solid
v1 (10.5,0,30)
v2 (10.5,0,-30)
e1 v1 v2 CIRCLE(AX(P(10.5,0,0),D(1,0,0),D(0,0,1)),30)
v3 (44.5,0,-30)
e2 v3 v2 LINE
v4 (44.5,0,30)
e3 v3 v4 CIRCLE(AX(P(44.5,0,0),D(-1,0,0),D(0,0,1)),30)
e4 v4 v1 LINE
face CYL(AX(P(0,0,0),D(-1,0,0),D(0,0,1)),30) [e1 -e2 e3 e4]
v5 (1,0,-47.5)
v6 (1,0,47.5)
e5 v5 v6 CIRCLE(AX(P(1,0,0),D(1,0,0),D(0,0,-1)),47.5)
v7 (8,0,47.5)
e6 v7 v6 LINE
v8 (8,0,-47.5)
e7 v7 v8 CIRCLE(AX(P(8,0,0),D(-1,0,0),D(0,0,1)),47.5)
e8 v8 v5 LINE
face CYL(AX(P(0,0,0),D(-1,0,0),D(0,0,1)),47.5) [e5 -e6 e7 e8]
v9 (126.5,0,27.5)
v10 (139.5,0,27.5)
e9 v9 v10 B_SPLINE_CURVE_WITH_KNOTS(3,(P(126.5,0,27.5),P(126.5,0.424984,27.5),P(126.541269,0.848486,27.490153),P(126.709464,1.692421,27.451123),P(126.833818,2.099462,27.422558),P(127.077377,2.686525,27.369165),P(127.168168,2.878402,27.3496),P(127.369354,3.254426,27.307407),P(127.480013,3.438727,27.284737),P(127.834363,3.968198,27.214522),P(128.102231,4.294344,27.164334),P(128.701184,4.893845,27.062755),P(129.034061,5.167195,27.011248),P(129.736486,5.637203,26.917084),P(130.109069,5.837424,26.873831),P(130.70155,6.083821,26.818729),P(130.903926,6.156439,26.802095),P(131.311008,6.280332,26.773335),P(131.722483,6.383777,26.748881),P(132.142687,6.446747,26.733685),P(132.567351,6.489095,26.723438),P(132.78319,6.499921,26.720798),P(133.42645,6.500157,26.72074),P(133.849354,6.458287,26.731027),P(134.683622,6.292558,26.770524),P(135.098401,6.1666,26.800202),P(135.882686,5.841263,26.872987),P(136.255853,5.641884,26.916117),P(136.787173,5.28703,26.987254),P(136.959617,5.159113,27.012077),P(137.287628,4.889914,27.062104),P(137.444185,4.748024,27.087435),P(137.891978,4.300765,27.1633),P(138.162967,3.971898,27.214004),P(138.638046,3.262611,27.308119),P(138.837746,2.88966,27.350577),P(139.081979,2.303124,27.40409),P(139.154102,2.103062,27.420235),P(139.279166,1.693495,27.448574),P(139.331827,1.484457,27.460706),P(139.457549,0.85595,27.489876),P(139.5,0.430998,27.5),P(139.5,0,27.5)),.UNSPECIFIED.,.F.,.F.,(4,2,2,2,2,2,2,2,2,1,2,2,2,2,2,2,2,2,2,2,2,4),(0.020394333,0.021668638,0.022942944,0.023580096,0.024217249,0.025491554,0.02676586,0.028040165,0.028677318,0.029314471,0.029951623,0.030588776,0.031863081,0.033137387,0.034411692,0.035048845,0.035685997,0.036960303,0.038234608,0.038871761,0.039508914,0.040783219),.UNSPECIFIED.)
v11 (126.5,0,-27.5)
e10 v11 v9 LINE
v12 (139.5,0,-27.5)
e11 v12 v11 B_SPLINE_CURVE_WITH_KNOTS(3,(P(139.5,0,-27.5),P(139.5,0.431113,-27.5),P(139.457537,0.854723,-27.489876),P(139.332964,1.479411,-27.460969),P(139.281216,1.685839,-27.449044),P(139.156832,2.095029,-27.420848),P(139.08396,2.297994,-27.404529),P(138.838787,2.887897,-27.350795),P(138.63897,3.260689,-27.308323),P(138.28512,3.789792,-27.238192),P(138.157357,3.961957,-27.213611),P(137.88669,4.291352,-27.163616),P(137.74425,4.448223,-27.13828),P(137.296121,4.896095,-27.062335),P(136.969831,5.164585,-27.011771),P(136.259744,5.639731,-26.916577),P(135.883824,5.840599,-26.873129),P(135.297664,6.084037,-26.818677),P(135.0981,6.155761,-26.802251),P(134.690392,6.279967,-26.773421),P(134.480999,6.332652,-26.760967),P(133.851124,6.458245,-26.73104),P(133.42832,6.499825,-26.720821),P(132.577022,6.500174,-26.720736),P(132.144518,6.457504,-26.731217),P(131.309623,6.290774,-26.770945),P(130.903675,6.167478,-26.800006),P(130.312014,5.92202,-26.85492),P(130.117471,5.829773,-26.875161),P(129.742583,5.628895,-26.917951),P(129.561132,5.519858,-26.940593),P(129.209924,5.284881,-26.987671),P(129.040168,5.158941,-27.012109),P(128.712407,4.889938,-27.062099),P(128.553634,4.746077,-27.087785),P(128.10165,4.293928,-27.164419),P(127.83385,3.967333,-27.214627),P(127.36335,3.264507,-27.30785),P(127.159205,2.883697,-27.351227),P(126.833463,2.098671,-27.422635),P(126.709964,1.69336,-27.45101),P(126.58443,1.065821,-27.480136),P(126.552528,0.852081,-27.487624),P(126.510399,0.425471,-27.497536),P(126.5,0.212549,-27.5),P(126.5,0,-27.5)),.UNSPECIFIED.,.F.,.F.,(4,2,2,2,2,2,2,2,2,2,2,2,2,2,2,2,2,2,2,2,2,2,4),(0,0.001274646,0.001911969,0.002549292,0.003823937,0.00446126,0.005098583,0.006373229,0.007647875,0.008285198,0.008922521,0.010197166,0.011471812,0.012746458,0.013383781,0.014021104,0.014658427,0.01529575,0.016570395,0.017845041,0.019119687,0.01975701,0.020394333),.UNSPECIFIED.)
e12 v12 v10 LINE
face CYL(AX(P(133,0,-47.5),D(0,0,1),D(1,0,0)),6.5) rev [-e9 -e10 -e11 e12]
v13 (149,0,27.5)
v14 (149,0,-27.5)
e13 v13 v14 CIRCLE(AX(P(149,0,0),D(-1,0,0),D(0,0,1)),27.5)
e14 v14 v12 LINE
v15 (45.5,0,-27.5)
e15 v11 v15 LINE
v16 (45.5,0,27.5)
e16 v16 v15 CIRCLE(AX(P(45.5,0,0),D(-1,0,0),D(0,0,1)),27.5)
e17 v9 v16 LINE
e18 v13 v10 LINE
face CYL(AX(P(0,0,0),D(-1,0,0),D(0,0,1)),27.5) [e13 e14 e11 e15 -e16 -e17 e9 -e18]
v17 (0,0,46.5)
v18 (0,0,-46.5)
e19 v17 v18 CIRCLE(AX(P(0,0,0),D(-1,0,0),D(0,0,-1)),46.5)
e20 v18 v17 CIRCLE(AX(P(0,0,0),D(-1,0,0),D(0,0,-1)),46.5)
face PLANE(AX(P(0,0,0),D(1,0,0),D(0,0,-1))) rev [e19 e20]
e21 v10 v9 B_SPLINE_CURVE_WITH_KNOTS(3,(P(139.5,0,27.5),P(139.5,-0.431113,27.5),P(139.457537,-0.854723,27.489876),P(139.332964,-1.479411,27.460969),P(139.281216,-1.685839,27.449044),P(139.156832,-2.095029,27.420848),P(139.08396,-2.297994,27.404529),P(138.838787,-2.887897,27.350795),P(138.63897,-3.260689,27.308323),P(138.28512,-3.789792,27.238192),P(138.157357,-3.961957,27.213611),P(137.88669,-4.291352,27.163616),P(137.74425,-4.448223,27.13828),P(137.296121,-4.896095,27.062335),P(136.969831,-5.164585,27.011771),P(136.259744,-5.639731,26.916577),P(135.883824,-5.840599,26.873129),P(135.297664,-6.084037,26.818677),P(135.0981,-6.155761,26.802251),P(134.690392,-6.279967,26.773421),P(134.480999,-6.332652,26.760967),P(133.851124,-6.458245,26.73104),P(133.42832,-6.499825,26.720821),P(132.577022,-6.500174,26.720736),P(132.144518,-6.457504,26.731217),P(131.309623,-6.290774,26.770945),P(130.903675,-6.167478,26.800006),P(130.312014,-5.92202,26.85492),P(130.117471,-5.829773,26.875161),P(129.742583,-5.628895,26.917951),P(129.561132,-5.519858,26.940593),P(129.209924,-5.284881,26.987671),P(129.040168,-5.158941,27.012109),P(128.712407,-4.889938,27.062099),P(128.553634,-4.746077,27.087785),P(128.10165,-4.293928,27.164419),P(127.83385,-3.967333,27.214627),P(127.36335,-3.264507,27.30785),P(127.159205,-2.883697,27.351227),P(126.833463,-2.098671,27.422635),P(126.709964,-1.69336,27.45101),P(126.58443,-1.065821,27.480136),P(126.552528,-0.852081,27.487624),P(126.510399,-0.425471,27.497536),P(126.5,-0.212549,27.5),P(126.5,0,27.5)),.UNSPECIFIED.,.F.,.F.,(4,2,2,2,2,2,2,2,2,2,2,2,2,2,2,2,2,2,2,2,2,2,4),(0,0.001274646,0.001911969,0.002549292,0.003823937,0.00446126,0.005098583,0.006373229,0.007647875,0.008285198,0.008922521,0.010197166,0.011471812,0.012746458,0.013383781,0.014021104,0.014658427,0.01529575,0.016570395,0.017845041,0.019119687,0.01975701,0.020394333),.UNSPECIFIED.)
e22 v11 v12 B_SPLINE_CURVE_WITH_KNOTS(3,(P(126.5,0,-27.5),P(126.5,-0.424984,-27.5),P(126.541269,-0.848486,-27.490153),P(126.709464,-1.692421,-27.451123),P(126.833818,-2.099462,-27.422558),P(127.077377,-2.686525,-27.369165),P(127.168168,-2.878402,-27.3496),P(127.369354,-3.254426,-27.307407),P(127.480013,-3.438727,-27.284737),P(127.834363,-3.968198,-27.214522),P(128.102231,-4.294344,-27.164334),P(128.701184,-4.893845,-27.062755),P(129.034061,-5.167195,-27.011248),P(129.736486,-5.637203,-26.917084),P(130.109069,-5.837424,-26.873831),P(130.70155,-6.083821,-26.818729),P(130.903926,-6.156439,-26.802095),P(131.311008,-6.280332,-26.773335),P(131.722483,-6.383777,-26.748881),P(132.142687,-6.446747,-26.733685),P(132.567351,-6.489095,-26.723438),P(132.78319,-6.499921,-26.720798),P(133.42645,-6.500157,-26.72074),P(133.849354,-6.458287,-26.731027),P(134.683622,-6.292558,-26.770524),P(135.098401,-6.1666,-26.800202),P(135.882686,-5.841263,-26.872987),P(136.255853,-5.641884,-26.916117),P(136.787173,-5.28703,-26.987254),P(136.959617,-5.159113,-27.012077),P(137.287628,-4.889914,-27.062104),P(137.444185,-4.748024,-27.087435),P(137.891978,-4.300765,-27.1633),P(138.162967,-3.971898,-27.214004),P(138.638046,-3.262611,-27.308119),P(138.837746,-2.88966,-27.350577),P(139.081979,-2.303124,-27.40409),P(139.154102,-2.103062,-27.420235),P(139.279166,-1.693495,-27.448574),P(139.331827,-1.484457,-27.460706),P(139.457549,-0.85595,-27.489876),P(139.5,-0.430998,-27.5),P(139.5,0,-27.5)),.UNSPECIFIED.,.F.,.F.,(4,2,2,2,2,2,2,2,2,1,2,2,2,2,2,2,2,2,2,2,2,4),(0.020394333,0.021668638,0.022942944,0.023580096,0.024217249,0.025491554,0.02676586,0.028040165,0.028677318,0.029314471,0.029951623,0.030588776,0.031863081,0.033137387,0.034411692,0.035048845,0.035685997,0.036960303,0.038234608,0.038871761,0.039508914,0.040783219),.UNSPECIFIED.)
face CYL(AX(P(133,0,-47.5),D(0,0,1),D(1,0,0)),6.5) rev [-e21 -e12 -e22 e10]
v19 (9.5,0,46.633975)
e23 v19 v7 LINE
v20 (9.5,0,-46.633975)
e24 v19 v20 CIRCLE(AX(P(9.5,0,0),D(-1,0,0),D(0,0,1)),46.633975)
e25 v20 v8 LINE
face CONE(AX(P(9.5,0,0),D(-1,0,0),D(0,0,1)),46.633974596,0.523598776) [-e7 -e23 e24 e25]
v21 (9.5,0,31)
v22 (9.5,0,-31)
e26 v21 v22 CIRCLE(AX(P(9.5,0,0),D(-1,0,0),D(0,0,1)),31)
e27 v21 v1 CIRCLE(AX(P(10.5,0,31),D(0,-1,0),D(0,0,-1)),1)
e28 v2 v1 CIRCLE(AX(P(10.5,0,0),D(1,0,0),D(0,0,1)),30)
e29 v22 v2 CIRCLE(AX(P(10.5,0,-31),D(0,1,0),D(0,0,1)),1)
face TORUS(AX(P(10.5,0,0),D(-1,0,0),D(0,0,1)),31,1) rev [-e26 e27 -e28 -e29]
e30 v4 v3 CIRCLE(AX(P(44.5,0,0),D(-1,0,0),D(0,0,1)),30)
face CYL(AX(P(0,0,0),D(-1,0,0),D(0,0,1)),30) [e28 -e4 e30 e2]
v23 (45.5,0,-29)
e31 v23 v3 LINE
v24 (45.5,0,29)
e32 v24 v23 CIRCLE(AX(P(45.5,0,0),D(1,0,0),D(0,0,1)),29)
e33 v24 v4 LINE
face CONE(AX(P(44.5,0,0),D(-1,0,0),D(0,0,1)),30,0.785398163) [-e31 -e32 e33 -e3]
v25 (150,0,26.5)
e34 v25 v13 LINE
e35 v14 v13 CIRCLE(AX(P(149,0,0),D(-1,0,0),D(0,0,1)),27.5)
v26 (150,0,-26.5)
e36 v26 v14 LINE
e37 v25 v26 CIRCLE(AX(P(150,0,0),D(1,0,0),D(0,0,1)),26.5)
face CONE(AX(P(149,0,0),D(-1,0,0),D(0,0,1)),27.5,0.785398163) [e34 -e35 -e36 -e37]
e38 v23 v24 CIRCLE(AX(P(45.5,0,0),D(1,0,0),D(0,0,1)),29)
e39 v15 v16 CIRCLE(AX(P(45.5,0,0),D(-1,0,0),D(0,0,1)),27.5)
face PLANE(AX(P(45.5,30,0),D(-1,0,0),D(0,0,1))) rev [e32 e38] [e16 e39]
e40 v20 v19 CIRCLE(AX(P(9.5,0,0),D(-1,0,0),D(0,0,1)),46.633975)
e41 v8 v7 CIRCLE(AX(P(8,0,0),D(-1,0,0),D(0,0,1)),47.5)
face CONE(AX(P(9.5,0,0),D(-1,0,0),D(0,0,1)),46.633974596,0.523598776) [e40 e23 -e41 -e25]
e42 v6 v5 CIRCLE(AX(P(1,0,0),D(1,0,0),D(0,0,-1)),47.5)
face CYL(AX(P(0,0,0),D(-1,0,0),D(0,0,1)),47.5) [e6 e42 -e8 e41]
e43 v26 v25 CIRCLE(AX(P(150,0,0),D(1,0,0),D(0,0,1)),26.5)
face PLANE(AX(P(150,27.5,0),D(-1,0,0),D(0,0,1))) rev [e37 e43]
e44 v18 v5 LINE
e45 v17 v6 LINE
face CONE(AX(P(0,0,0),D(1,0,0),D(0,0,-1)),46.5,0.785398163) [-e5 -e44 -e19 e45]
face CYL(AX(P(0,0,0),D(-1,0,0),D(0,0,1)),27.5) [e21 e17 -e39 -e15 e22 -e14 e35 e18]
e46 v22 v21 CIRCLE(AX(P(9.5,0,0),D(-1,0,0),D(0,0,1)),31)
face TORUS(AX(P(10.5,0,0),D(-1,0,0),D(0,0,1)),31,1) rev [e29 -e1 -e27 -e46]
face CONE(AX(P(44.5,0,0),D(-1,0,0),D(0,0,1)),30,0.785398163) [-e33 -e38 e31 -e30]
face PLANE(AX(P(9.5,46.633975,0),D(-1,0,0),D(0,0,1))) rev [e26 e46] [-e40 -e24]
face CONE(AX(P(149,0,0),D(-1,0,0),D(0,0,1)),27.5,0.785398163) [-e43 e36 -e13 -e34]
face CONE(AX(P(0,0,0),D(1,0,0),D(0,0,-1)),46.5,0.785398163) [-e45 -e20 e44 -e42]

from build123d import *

# Parameters (mm, degrees)
FILLET1_R               = 1
CHAMFER1_SIZE           = 1
CUT_EXTRUDE1_DEPTH      = 165.354799139
CUT_EXTRUDE1_DEPTH_BACK = 165.354799139
SKETCH2_R               = 6.5


with BuildPart() as part:
    # Sketch1 → Revolve1 (revolve)
    with BuildSketch(Plane.XY, mode=Mode.PRIVATE) as revolve1_sk:
        Polygon((0, 0), (0, 47.5), (8, 47.5), (9.5, 46.633974596), (9.5, 30), (45.5, 30), (45.5, 27.5), (150, 27.5), (150, 0), align=None)
    revolve(revolve1_sk.sketch.rotate(Axis((0, 0, 0), (1, 0, 0)), 90), axis=Axis((0, 0, 0), (1, 0, 0)))

    # Fillet1
    fillet1_edges = [part.edges().sort_by_distance(p)[0] for p in [
        (9.5, 0, -30),
    ]]
    fillet(fillet1_edges, radius=FILLET1_R)

    # Chamfer1
    chamfer1_edges = [part.edges().sort_by_distance(p)[0] for p in [
        (150, 0, -27.5),
        (45.5, 0, -30),
        (0, 0, -47.5),
    ]]
    chamfer(chamfer1_edges, length=CHAMFER1_SIZE)

    # Sketch2 → Cut-Extrude1 (cut, two sides: drawn at the far end of the back side and taken through both)
    with BuildSketch(Plane.XY.offset(-CUT_EXTRUDE1_DEPTH_BACK)):
        with Locations((133, 0)):
            Circle(SKETCH2_R)
    extrude(amount=CUT_EXTRUDE1_DEPTH + CUT_EXTRUDE1_DEPTH_BACK, mode=Mode.SUBTRACT)


solid = part.part
